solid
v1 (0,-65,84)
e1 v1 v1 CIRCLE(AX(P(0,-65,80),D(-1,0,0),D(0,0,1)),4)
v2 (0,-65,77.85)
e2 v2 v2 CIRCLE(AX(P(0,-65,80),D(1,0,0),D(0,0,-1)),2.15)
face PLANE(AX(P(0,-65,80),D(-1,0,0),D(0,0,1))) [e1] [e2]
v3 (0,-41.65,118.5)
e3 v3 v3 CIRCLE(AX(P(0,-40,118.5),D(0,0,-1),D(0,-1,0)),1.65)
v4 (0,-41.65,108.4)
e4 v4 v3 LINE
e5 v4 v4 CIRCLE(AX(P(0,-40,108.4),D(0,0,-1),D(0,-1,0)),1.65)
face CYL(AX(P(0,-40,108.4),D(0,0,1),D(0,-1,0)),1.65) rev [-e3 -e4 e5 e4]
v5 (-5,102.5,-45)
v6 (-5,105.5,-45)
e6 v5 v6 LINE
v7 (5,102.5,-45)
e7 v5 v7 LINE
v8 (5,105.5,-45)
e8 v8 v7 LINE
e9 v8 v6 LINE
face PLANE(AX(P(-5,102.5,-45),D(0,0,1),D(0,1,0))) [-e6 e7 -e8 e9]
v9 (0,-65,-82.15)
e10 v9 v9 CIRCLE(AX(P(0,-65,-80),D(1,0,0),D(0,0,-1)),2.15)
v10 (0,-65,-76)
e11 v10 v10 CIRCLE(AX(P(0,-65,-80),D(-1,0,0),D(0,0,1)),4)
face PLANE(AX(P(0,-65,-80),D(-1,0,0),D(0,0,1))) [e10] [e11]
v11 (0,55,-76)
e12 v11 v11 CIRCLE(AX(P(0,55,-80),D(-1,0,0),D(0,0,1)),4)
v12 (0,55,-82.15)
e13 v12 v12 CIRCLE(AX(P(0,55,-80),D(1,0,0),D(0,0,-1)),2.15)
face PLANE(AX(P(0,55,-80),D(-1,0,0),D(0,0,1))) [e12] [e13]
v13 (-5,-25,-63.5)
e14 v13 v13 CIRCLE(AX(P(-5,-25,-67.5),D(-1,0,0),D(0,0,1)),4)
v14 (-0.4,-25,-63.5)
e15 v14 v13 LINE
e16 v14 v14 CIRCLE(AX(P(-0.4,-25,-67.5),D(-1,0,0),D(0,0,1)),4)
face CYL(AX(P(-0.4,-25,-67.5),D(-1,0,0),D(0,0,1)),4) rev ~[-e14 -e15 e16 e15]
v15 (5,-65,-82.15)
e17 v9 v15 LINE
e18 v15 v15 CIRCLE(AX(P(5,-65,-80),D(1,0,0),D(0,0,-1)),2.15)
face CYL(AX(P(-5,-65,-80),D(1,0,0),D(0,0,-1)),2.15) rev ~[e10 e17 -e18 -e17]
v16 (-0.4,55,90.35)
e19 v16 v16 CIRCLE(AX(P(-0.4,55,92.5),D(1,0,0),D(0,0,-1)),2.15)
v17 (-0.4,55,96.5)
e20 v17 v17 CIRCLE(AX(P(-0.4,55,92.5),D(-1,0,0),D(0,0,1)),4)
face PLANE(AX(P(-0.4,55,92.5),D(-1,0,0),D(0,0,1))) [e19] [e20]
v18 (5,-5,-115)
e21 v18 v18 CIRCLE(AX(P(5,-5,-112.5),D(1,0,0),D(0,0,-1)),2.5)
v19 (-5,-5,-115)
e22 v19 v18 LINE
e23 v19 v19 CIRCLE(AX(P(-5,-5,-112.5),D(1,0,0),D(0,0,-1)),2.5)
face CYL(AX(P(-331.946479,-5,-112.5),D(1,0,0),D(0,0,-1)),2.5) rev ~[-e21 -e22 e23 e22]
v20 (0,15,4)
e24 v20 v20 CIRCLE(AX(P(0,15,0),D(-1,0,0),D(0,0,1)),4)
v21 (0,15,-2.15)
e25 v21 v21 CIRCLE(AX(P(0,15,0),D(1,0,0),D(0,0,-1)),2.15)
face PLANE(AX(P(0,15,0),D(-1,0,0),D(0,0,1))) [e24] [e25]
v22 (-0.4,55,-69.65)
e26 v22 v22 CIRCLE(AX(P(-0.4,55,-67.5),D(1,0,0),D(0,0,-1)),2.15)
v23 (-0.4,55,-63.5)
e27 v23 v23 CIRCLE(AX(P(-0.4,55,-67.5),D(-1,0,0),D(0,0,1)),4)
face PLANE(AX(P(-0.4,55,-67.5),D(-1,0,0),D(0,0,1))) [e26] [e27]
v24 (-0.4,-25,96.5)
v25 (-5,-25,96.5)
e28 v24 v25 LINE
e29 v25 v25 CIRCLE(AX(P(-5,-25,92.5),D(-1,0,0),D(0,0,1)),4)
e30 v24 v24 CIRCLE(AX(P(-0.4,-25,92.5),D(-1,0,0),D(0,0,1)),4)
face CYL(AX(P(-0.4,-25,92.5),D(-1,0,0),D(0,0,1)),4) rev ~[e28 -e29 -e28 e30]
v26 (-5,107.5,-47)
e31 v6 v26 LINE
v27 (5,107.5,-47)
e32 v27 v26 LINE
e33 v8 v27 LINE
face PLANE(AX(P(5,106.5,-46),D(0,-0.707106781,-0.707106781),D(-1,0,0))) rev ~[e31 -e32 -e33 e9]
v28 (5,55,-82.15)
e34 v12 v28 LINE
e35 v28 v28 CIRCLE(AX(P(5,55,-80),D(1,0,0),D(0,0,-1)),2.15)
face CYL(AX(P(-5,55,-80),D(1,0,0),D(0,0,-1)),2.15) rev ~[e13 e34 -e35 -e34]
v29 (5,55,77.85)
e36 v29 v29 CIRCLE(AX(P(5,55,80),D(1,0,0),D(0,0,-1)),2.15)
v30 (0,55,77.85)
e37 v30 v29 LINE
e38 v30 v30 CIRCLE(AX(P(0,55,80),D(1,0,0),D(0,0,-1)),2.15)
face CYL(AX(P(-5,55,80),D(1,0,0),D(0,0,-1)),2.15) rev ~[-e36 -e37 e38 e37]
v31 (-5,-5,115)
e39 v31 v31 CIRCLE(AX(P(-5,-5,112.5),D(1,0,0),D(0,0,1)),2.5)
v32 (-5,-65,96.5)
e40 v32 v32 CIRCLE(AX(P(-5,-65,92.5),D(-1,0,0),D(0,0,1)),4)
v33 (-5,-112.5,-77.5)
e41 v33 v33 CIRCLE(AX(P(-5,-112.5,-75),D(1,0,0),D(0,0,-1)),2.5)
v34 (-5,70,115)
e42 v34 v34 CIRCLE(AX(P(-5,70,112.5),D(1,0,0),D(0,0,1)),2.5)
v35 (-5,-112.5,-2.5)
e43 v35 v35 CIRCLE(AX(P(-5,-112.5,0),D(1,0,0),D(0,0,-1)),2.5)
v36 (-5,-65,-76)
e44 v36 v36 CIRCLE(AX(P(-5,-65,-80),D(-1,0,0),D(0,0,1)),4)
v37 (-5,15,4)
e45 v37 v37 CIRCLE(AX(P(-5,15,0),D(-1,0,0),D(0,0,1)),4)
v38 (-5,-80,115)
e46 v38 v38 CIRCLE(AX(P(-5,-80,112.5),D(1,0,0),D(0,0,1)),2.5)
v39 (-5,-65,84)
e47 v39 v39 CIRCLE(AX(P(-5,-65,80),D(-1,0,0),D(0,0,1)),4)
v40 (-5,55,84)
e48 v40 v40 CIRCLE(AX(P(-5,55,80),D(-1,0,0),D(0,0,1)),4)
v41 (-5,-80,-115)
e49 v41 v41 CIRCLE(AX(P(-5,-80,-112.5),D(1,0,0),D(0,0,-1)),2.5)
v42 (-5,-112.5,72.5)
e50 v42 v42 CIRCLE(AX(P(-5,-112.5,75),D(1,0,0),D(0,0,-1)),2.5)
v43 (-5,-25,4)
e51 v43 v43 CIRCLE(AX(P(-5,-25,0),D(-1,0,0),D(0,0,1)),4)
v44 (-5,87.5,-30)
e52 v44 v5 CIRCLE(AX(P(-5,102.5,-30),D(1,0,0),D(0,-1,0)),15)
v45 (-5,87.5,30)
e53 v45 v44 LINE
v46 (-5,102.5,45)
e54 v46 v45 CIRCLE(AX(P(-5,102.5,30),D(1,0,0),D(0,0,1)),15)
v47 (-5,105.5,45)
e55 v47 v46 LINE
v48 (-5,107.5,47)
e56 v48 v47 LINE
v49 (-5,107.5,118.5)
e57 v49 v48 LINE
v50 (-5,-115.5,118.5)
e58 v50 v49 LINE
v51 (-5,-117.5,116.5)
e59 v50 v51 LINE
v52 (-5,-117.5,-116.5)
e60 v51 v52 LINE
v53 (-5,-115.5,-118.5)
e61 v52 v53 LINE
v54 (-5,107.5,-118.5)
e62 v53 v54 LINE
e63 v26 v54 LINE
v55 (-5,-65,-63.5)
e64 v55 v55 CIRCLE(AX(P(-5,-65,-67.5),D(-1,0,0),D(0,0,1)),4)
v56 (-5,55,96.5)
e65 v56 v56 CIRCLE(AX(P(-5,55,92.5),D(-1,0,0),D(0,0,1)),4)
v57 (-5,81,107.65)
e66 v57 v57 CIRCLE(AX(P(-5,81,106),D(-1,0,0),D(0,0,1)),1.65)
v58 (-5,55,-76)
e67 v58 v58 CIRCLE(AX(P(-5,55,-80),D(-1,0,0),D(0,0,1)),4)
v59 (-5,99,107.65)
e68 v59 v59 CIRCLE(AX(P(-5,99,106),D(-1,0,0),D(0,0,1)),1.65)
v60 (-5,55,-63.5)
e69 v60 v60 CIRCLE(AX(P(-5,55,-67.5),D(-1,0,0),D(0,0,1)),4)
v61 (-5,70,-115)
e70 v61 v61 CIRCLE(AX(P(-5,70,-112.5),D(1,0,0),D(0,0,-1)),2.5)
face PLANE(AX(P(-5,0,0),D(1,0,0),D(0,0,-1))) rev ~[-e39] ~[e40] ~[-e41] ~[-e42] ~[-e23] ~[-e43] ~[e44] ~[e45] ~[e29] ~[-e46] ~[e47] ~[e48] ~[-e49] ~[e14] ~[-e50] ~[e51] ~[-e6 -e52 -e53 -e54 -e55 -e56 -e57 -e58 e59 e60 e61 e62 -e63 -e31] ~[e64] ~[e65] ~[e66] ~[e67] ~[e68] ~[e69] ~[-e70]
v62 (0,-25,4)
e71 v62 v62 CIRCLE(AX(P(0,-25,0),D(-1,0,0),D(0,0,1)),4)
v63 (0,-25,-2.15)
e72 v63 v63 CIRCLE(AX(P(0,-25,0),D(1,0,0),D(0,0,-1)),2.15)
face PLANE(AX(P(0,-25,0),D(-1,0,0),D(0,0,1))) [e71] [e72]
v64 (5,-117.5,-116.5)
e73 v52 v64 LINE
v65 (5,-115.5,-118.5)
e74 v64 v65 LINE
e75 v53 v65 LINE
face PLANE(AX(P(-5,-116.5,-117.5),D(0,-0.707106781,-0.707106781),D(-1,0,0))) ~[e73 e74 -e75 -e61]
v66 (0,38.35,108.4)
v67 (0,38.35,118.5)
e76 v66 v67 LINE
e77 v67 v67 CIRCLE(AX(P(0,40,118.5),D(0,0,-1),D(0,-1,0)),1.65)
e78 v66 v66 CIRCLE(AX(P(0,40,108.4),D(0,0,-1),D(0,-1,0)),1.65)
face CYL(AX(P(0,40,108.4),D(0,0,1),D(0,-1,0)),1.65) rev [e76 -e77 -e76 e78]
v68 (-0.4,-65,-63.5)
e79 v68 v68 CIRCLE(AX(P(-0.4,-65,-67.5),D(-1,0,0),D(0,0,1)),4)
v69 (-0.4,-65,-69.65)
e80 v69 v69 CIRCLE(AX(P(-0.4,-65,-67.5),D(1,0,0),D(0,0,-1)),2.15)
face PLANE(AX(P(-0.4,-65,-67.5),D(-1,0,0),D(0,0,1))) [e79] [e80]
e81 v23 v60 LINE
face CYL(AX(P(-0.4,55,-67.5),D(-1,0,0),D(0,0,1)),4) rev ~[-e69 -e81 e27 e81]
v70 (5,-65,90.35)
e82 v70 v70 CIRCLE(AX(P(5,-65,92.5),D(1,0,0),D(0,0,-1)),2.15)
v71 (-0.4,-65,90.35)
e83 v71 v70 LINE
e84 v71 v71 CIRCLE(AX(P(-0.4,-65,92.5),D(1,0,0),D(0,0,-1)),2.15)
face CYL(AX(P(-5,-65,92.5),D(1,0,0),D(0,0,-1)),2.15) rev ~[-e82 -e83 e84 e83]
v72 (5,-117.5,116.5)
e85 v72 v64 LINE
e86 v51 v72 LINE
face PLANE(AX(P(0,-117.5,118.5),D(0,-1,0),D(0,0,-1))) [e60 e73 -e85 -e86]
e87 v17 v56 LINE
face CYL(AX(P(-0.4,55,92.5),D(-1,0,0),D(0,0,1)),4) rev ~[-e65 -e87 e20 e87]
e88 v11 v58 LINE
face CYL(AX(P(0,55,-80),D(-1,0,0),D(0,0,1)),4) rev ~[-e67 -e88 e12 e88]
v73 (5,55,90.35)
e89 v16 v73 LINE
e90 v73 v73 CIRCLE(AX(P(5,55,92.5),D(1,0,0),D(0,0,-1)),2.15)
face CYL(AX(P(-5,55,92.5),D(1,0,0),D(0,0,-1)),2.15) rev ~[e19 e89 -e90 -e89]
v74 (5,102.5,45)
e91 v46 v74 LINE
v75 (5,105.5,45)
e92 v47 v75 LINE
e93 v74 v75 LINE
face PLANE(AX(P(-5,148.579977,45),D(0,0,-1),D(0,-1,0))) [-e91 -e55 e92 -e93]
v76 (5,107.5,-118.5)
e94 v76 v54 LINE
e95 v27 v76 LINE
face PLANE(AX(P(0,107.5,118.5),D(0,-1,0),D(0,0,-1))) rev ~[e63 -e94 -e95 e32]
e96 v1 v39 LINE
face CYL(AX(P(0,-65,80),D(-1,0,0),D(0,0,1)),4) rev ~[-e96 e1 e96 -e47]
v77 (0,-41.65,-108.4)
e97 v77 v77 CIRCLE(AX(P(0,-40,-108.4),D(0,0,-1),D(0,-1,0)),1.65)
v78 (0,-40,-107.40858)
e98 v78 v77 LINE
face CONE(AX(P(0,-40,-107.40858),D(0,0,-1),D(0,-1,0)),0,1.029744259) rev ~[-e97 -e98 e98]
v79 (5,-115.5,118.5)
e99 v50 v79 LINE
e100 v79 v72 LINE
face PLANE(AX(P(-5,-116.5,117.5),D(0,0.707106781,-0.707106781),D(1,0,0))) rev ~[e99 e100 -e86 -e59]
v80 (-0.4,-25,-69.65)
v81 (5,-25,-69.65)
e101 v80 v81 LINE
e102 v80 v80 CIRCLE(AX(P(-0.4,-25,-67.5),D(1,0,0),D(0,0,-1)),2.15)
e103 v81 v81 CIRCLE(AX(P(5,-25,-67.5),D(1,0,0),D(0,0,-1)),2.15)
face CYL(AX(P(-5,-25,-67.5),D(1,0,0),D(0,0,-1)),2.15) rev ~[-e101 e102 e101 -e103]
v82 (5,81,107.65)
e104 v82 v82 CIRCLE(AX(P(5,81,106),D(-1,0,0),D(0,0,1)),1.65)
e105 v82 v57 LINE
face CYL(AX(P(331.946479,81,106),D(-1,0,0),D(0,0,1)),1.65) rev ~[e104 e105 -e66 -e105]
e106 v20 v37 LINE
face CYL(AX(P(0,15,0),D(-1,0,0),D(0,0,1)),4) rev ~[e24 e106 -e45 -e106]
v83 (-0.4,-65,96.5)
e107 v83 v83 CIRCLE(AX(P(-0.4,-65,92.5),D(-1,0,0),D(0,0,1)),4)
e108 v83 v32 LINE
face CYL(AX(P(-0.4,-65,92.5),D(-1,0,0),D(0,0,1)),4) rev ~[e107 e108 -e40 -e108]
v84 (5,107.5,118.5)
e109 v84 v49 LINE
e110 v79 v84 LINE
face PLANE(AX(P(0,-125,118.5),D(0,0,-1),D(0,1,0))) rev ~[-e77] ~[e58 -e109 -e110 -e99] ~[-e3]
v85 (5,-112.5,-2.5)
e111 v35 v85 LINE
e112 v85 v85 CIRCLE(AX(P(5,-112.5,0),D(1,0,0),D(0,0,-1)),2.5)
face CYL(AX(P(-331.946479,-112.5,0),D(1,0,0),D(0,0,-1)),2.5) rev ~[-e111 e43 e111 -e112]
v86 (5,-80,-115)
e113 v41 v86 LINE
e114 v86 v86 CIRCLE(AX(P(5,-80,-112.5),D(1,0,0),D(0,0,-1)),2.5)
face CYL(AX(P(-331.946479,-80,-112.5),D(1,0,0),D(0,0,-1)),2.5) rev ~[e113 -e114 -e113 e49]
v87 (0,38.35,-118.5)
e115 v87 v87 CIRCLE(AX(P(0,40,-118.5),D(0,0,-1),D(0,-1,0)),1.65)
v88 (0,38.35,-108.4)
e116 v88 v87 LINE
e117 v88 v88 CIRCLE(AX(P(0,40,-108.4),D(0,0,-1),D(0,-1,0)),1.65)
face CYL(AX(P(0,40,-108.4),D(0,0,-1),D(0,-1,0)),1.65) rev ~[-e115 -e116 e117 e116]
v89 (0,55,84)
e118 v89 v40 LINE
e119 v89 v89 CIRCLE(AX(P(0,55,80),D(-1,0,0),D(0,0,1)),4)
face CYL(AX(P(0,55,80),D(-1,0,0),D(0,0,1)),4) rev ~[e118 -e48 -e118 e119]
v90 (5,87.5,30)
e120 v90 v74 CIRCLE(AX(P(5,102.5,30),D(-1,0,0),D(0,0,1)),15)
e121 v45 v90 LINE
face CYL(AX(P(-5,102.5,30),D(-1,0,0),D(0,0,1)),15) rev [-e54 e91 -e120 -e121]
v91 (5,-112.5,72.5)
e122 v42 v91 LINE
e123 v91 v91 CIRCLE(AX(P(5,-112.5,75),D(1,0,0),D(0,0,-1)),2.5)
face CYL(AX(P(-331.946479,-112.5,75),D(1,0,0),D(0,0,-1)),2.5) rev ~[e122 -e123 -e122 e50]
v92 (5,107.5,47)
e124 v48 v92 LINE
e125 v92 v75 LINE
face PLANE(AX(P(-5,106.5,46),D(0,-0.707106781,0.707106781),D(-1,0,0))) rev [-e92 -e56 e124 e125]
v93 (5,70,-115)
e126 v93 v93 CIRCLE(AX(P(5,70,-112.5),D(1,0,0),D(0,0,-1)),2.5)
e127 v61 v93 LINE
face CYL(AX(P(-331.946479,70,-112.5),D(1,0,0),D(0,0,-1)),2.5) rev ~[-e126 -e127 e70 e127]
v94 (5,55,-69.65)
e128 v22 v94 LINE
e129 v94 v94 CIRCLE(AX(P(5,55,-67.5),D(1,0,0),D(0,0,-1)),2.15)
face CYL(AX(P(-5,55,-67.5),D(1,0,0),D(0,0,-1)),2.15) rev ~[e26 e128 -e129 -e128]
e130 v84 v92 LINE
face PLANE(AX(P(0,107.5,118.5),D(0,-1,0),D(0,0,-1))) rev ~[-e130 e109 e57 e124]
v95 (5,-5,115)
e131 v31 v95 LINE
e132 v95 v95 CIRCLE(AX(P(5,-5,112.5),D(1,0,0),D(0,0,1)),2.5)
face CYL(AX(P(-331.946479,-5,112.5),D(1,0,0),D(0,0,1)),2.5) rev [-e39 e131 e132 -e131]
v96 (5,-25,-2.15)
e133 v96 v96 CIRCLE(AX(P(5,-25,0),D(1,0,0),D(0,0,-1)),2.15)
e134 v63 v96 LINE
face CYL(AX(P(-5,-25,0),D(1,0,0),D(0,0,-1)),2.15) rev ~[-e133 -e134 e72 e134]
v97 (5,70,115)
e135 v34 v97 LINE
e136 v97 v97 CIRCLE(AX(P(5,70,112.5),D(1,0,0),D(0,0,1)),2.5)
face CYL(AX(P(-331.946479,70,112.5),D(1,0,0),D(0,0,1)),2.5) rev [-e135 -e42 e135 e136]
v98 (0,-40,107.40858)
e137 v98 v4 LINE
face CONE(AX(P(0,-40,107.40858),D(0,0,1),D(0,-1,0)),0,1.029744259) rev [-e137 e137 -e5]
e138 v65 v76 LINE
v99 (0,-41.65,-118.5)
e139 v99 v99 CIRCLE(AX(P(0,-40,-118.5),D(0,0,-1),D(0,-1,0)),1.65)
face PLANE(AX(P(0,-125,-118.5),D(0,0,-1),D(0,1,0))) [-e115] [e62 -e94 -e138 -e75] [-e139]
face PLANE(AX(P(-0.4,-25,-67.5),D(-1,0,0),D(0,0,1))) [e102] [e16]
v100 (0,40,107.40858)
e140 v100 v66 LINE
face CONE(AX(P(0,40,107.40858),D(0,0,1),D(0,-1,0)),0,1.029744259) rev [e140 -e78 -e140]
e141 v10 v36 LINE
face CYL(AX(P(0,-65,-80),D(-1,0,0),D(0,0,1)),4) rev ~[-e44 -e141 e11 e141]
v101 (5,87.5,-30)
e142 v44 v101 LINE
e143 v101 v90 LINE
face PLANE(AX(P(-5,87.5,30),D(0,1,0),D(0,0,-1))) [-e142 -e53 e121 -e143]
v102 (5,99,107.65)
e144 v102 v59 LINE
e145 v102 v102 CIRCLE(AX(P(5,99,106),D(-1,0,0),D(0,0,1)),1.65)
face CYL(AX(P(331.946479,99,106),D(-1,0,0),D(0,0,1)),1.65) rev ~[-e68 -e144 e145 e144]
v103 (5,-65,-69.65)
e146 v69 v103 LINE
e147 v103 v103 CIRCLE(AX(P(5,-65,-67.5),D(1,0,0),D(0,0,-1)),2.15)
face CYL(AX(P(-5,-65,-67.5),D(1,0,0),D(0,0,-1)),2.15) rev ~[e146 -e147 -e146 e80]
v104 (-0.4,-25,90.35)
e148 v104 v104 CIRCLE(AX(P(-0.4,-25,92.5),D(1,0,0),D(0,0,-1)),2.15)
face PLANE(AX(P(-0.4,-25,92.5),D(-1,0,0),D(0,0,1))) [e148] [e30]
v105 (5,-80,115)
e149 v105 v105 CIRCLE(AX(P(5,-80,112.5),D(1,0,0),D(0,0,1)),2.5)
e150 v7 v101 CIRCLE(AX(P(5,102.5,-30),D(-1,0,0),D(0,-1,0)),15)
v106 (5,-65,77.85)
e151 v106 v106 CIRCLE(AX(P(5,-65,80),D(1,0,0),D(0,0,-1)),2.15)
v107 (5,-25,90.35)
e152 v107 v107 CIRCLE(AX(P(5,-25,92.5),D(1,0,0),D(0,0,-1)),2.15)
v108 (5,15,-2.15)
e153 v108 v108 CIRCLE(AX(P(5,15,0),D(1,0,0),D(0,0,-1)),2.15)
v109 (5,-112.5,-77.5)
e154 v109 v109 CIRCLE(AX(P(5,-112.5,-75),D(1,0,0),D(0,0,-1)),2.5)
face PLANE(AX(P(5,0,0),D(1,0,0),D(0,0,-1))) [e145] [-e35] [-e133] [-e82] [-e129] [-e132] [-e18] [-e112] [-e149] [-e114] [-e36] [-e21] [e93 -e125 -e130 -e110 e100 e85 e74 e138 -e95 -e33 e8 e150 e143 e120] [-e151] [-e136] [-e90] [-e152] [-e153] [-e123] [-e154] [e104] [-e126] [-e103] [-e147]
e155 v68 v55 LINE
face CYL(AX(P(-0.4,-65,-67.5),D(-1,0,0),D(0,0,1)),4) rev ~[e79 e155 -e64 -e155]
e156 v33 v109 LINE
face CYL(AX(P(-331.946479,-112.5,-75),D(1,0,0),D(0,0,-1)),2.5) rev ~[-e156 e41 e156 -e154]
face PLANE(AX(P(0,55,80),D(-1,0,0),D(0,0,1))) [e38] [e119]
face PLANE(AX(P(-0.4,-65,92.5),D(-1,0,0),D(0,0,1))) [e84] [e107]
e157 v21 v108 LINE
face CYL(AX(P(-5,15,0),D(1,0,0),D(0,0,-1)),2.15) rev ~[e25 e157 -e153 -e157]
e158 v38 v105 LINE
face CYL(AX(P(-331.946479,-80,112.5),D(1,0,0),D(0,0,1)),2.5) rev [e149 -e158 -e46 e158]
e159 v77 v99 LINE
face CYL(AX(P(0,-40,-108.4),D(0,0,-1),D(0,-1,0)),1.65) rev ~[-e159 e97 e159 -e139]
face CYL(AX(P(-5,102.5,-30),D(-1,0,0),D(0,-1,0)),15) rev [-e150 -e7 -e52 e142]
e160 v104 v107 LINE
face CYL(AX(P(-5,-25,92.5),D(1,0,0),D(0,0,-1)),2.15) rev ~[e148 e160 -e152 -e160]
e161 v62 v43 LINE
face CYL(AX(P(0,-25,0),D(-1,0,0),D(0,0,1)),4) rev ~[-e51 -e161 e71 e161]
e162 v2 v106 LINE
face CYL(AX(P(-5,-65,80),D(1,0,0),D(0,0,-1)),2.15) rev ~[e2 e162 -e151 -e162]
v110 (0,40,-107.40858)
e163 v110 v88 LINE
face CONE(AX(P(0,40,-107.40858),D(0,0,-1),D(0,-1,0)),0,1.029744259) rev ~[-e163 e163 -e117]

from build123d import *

# Parameters (mm, degrees)
SKETCH_1_W                  = 237
SKETCH_1_H                  = 250
EXTRUDE_1_DEPTH             = 5
MOVE_FACE_1_BY              = 17.5
MOVE_FACE_2_BY              = 7.5
HOLE_WIZARD_M4_1_AT_2_COUNT = 2
HOLE_WIZARD_M4_1_AT_2_PITCH = 80
HOLE_WIZARD_M4_2_D          = 3.3
HOLE_WIZARD_M6_1_D          = 5
HOLE_WIZARD_M6_2_D          = 5
CHAMFER_1_SIZE              = 2
CUT_EXTRUDE_1_DEPTH         = 71
CHAMFER_2_SIZE              = 2
HOLE_WIZARD_1_D             = 4.3
HOLE_WIZARD_1_CBORE_D       = 8
HOLE_WIZARD_1_CBORE_DEPTH   = 4.6
HOLE_WIZARD_1_2_D           = 4.3
HOLE_WIZARD_1_2_CBORE_D     = 8
HOLE_WIZARD_1_2_CBORE_DEPTH = 5


with BuildPart() as part:
    # 草图1 → 凸台-拉伸1 (new, symmetric)
    with BuildSketch(Plane(origin=(0, 0, 0), x_dir=(0, 0, -1), z_dir=(1, 0, 0))):
        Rectangle(SKETCH_1_W, SKETCH_1_H)
    extrude(amount=EXTRUDE_1_DEPTH, both=True)

    # Move Face 1: a face moved inward by 17.5
    extrude(part.faces().sort_by_distance((0, 125, 0))[0], amount=MOVE_FACE_1_BY, dir=(0, -1, 0), mode=Mode.SUBTRACT)

    # Move Face 2: a face moved inward by 7.5
    extrude(part.faces().sort_by_distance((0, -125, 0))[0], amount=MOVE_FACE_2_BY, dir=(0, 1, 0), mode=Mode.SUBTRACT)

    # 草图3 → M4 螺纹孔1 (revolve, cut)
    with BuildSketch(Plane(origin=(0, -40, 118.5), x_dir=(0, -1, 0), z_dir=(1, 0, 0))):
        Polygon((0, 0), (0, 11.091420021), (1.65, 10.1), (1.65, 0), align=None)
    hole_wizard_m4_1 = revolve(axis=Axis((0, -40, 124.85), (0, 0, -1)), mode=Mode.SUBTRACT)

    # M4 螺纹孔1 at 2: M4 螺纹孔1 ×2
    with Locations(*[(0, i * HOLE_WIZARD_M4_1_AT_2_PITCH, 0) for i in range(1, HOLE_WIZARD_M4_1_AT_2_COUNT)]):
        add(hole_wizard_m4_1, mode=Mode.SUBTRACT)

    # 镜向1: M4 螺纹孔1 across plane
    add(hole_wizard_m4_1.mirror(Plane.XY), mode=Mode.SUBTRACT)

    # 镜向1 copy 1 sketch → 镜向1 copy 1 (revolve, cut)
    with BuildSketch(Plane(origin=(0, 40, -118.5), x_dir=(0, -1, 0), z_dir=(1, 0, 0))):
        Polygon((0, 0), (0, -11.091420021), (1.65, -10.1), (1.65, 0), align=None)
    revolve(axis=Axis((0, 40, -124.85), (0, 0, -1)), mode=Mode.SUBTRACT)

    # M4 螺纹孔2 (through all)
    with Locations(Plane(origin=(5, 0, 0), x_dir=(0, 0, -1), z_dir=(1, 0, 0))):
        with Locations((-106, 99), (-106, 81)):
            Hole(HOLE_WIZARD_M4_2_D / 2)

    # M6 螺纹孔1 (through all)
    with Locations(Plane.ZY.offset(5)):
        with Locations((-112.5, 70), (-112.5, -5), (-112.5, -80)):
            hole_wizard_m6_1 = Hole(HOLE_WIZARD_M6_1_D / 2)

    # 镜向2: M6 螺纹孔1 across plane
    add(hole_wizard_m6_1.mirror(Plane.XY), mode=Mode.SUBTRACT)

    # M6 螺纹孔2 (through all)
    with Locations(Plane.ZY.offset(5)):
        with Locations((75, -112.5), (0, -112.5), (-75, -112.5)):
            Hole(HOLE_WIZARD_M6_2_D / 2)

    # 倒角1
    chamfer_1_edges = [part.edges().sort_by_distance(p)[0] for p in [
        (0, -117.5, -118.5),
        (0, -117.5, 118.5),
    ]]
    chamfer(chamfer_1_edges, length=CHAMFER_1_SIZE)

    # 草图11 → 切除-拉伸1 (cut)
    with BuildSketch(Plane.ZY.offset(5)):
        with BuildLine():
            Line((-45, 148.579976686), (45, 148.579976686))
            Line((45, 148.579976686), (45, 102.5))
            ThreePointArc((45, 102.5), (40.606601718, 91.893398282), (30, 87.5))
            Line((30, 87.5), (-30, 87.5))
            ThreePointArc((-30, 87.5), (-40.606601718, 91.893398282), (-45, 102.5))
            Line((-45, 102.5), (-45, 148.579976686))
        make_face()
    extrude(amount=-CUT_EXTRUDE_1_DEPTH, mode=Mode.SUBTRACT)

    # 倒角2
    chamfer_2_edges = [part.edges().sort_by_distance(p)[0] for p in [
        (0, 107.5, -45),
        (0, 107.5, 45),
    ]]
    chamfer(chamfer_2_edges, length=CHAMFER_2_SIZE)

    # Hole Wizard 1 (through all)
    with Locations(Plane.ZY.offset(5)):
        with Locations((-67.5, 55), (92.5, 55), (92.5, -65), (-67.5, -65), (-67.5, -25), (92.5, -25)):
            CounterBoreHole(HOLE_WIZARD_1_D / 2, HOLE_WIZARD_1_CBORE_D / 2, HOLE_WIZARD_1_CBORE_DEPTH)

    # Hole Wizard 1 2 (through all)
    with Locations(Plane.ZY.offset(5)):
        with Locations((80, 55), (-80, 55), (-80, -65), (80, -65), (0, -25), (0, 15)):
            CounterBoreHole(HOLE_WIZARD_1_2_D / 2, HOLE_WIZARD_1_2_CBORE_D / 2, HOLE_WIZARD_1_2_CBORE_DEPTH)


solid = part.part
